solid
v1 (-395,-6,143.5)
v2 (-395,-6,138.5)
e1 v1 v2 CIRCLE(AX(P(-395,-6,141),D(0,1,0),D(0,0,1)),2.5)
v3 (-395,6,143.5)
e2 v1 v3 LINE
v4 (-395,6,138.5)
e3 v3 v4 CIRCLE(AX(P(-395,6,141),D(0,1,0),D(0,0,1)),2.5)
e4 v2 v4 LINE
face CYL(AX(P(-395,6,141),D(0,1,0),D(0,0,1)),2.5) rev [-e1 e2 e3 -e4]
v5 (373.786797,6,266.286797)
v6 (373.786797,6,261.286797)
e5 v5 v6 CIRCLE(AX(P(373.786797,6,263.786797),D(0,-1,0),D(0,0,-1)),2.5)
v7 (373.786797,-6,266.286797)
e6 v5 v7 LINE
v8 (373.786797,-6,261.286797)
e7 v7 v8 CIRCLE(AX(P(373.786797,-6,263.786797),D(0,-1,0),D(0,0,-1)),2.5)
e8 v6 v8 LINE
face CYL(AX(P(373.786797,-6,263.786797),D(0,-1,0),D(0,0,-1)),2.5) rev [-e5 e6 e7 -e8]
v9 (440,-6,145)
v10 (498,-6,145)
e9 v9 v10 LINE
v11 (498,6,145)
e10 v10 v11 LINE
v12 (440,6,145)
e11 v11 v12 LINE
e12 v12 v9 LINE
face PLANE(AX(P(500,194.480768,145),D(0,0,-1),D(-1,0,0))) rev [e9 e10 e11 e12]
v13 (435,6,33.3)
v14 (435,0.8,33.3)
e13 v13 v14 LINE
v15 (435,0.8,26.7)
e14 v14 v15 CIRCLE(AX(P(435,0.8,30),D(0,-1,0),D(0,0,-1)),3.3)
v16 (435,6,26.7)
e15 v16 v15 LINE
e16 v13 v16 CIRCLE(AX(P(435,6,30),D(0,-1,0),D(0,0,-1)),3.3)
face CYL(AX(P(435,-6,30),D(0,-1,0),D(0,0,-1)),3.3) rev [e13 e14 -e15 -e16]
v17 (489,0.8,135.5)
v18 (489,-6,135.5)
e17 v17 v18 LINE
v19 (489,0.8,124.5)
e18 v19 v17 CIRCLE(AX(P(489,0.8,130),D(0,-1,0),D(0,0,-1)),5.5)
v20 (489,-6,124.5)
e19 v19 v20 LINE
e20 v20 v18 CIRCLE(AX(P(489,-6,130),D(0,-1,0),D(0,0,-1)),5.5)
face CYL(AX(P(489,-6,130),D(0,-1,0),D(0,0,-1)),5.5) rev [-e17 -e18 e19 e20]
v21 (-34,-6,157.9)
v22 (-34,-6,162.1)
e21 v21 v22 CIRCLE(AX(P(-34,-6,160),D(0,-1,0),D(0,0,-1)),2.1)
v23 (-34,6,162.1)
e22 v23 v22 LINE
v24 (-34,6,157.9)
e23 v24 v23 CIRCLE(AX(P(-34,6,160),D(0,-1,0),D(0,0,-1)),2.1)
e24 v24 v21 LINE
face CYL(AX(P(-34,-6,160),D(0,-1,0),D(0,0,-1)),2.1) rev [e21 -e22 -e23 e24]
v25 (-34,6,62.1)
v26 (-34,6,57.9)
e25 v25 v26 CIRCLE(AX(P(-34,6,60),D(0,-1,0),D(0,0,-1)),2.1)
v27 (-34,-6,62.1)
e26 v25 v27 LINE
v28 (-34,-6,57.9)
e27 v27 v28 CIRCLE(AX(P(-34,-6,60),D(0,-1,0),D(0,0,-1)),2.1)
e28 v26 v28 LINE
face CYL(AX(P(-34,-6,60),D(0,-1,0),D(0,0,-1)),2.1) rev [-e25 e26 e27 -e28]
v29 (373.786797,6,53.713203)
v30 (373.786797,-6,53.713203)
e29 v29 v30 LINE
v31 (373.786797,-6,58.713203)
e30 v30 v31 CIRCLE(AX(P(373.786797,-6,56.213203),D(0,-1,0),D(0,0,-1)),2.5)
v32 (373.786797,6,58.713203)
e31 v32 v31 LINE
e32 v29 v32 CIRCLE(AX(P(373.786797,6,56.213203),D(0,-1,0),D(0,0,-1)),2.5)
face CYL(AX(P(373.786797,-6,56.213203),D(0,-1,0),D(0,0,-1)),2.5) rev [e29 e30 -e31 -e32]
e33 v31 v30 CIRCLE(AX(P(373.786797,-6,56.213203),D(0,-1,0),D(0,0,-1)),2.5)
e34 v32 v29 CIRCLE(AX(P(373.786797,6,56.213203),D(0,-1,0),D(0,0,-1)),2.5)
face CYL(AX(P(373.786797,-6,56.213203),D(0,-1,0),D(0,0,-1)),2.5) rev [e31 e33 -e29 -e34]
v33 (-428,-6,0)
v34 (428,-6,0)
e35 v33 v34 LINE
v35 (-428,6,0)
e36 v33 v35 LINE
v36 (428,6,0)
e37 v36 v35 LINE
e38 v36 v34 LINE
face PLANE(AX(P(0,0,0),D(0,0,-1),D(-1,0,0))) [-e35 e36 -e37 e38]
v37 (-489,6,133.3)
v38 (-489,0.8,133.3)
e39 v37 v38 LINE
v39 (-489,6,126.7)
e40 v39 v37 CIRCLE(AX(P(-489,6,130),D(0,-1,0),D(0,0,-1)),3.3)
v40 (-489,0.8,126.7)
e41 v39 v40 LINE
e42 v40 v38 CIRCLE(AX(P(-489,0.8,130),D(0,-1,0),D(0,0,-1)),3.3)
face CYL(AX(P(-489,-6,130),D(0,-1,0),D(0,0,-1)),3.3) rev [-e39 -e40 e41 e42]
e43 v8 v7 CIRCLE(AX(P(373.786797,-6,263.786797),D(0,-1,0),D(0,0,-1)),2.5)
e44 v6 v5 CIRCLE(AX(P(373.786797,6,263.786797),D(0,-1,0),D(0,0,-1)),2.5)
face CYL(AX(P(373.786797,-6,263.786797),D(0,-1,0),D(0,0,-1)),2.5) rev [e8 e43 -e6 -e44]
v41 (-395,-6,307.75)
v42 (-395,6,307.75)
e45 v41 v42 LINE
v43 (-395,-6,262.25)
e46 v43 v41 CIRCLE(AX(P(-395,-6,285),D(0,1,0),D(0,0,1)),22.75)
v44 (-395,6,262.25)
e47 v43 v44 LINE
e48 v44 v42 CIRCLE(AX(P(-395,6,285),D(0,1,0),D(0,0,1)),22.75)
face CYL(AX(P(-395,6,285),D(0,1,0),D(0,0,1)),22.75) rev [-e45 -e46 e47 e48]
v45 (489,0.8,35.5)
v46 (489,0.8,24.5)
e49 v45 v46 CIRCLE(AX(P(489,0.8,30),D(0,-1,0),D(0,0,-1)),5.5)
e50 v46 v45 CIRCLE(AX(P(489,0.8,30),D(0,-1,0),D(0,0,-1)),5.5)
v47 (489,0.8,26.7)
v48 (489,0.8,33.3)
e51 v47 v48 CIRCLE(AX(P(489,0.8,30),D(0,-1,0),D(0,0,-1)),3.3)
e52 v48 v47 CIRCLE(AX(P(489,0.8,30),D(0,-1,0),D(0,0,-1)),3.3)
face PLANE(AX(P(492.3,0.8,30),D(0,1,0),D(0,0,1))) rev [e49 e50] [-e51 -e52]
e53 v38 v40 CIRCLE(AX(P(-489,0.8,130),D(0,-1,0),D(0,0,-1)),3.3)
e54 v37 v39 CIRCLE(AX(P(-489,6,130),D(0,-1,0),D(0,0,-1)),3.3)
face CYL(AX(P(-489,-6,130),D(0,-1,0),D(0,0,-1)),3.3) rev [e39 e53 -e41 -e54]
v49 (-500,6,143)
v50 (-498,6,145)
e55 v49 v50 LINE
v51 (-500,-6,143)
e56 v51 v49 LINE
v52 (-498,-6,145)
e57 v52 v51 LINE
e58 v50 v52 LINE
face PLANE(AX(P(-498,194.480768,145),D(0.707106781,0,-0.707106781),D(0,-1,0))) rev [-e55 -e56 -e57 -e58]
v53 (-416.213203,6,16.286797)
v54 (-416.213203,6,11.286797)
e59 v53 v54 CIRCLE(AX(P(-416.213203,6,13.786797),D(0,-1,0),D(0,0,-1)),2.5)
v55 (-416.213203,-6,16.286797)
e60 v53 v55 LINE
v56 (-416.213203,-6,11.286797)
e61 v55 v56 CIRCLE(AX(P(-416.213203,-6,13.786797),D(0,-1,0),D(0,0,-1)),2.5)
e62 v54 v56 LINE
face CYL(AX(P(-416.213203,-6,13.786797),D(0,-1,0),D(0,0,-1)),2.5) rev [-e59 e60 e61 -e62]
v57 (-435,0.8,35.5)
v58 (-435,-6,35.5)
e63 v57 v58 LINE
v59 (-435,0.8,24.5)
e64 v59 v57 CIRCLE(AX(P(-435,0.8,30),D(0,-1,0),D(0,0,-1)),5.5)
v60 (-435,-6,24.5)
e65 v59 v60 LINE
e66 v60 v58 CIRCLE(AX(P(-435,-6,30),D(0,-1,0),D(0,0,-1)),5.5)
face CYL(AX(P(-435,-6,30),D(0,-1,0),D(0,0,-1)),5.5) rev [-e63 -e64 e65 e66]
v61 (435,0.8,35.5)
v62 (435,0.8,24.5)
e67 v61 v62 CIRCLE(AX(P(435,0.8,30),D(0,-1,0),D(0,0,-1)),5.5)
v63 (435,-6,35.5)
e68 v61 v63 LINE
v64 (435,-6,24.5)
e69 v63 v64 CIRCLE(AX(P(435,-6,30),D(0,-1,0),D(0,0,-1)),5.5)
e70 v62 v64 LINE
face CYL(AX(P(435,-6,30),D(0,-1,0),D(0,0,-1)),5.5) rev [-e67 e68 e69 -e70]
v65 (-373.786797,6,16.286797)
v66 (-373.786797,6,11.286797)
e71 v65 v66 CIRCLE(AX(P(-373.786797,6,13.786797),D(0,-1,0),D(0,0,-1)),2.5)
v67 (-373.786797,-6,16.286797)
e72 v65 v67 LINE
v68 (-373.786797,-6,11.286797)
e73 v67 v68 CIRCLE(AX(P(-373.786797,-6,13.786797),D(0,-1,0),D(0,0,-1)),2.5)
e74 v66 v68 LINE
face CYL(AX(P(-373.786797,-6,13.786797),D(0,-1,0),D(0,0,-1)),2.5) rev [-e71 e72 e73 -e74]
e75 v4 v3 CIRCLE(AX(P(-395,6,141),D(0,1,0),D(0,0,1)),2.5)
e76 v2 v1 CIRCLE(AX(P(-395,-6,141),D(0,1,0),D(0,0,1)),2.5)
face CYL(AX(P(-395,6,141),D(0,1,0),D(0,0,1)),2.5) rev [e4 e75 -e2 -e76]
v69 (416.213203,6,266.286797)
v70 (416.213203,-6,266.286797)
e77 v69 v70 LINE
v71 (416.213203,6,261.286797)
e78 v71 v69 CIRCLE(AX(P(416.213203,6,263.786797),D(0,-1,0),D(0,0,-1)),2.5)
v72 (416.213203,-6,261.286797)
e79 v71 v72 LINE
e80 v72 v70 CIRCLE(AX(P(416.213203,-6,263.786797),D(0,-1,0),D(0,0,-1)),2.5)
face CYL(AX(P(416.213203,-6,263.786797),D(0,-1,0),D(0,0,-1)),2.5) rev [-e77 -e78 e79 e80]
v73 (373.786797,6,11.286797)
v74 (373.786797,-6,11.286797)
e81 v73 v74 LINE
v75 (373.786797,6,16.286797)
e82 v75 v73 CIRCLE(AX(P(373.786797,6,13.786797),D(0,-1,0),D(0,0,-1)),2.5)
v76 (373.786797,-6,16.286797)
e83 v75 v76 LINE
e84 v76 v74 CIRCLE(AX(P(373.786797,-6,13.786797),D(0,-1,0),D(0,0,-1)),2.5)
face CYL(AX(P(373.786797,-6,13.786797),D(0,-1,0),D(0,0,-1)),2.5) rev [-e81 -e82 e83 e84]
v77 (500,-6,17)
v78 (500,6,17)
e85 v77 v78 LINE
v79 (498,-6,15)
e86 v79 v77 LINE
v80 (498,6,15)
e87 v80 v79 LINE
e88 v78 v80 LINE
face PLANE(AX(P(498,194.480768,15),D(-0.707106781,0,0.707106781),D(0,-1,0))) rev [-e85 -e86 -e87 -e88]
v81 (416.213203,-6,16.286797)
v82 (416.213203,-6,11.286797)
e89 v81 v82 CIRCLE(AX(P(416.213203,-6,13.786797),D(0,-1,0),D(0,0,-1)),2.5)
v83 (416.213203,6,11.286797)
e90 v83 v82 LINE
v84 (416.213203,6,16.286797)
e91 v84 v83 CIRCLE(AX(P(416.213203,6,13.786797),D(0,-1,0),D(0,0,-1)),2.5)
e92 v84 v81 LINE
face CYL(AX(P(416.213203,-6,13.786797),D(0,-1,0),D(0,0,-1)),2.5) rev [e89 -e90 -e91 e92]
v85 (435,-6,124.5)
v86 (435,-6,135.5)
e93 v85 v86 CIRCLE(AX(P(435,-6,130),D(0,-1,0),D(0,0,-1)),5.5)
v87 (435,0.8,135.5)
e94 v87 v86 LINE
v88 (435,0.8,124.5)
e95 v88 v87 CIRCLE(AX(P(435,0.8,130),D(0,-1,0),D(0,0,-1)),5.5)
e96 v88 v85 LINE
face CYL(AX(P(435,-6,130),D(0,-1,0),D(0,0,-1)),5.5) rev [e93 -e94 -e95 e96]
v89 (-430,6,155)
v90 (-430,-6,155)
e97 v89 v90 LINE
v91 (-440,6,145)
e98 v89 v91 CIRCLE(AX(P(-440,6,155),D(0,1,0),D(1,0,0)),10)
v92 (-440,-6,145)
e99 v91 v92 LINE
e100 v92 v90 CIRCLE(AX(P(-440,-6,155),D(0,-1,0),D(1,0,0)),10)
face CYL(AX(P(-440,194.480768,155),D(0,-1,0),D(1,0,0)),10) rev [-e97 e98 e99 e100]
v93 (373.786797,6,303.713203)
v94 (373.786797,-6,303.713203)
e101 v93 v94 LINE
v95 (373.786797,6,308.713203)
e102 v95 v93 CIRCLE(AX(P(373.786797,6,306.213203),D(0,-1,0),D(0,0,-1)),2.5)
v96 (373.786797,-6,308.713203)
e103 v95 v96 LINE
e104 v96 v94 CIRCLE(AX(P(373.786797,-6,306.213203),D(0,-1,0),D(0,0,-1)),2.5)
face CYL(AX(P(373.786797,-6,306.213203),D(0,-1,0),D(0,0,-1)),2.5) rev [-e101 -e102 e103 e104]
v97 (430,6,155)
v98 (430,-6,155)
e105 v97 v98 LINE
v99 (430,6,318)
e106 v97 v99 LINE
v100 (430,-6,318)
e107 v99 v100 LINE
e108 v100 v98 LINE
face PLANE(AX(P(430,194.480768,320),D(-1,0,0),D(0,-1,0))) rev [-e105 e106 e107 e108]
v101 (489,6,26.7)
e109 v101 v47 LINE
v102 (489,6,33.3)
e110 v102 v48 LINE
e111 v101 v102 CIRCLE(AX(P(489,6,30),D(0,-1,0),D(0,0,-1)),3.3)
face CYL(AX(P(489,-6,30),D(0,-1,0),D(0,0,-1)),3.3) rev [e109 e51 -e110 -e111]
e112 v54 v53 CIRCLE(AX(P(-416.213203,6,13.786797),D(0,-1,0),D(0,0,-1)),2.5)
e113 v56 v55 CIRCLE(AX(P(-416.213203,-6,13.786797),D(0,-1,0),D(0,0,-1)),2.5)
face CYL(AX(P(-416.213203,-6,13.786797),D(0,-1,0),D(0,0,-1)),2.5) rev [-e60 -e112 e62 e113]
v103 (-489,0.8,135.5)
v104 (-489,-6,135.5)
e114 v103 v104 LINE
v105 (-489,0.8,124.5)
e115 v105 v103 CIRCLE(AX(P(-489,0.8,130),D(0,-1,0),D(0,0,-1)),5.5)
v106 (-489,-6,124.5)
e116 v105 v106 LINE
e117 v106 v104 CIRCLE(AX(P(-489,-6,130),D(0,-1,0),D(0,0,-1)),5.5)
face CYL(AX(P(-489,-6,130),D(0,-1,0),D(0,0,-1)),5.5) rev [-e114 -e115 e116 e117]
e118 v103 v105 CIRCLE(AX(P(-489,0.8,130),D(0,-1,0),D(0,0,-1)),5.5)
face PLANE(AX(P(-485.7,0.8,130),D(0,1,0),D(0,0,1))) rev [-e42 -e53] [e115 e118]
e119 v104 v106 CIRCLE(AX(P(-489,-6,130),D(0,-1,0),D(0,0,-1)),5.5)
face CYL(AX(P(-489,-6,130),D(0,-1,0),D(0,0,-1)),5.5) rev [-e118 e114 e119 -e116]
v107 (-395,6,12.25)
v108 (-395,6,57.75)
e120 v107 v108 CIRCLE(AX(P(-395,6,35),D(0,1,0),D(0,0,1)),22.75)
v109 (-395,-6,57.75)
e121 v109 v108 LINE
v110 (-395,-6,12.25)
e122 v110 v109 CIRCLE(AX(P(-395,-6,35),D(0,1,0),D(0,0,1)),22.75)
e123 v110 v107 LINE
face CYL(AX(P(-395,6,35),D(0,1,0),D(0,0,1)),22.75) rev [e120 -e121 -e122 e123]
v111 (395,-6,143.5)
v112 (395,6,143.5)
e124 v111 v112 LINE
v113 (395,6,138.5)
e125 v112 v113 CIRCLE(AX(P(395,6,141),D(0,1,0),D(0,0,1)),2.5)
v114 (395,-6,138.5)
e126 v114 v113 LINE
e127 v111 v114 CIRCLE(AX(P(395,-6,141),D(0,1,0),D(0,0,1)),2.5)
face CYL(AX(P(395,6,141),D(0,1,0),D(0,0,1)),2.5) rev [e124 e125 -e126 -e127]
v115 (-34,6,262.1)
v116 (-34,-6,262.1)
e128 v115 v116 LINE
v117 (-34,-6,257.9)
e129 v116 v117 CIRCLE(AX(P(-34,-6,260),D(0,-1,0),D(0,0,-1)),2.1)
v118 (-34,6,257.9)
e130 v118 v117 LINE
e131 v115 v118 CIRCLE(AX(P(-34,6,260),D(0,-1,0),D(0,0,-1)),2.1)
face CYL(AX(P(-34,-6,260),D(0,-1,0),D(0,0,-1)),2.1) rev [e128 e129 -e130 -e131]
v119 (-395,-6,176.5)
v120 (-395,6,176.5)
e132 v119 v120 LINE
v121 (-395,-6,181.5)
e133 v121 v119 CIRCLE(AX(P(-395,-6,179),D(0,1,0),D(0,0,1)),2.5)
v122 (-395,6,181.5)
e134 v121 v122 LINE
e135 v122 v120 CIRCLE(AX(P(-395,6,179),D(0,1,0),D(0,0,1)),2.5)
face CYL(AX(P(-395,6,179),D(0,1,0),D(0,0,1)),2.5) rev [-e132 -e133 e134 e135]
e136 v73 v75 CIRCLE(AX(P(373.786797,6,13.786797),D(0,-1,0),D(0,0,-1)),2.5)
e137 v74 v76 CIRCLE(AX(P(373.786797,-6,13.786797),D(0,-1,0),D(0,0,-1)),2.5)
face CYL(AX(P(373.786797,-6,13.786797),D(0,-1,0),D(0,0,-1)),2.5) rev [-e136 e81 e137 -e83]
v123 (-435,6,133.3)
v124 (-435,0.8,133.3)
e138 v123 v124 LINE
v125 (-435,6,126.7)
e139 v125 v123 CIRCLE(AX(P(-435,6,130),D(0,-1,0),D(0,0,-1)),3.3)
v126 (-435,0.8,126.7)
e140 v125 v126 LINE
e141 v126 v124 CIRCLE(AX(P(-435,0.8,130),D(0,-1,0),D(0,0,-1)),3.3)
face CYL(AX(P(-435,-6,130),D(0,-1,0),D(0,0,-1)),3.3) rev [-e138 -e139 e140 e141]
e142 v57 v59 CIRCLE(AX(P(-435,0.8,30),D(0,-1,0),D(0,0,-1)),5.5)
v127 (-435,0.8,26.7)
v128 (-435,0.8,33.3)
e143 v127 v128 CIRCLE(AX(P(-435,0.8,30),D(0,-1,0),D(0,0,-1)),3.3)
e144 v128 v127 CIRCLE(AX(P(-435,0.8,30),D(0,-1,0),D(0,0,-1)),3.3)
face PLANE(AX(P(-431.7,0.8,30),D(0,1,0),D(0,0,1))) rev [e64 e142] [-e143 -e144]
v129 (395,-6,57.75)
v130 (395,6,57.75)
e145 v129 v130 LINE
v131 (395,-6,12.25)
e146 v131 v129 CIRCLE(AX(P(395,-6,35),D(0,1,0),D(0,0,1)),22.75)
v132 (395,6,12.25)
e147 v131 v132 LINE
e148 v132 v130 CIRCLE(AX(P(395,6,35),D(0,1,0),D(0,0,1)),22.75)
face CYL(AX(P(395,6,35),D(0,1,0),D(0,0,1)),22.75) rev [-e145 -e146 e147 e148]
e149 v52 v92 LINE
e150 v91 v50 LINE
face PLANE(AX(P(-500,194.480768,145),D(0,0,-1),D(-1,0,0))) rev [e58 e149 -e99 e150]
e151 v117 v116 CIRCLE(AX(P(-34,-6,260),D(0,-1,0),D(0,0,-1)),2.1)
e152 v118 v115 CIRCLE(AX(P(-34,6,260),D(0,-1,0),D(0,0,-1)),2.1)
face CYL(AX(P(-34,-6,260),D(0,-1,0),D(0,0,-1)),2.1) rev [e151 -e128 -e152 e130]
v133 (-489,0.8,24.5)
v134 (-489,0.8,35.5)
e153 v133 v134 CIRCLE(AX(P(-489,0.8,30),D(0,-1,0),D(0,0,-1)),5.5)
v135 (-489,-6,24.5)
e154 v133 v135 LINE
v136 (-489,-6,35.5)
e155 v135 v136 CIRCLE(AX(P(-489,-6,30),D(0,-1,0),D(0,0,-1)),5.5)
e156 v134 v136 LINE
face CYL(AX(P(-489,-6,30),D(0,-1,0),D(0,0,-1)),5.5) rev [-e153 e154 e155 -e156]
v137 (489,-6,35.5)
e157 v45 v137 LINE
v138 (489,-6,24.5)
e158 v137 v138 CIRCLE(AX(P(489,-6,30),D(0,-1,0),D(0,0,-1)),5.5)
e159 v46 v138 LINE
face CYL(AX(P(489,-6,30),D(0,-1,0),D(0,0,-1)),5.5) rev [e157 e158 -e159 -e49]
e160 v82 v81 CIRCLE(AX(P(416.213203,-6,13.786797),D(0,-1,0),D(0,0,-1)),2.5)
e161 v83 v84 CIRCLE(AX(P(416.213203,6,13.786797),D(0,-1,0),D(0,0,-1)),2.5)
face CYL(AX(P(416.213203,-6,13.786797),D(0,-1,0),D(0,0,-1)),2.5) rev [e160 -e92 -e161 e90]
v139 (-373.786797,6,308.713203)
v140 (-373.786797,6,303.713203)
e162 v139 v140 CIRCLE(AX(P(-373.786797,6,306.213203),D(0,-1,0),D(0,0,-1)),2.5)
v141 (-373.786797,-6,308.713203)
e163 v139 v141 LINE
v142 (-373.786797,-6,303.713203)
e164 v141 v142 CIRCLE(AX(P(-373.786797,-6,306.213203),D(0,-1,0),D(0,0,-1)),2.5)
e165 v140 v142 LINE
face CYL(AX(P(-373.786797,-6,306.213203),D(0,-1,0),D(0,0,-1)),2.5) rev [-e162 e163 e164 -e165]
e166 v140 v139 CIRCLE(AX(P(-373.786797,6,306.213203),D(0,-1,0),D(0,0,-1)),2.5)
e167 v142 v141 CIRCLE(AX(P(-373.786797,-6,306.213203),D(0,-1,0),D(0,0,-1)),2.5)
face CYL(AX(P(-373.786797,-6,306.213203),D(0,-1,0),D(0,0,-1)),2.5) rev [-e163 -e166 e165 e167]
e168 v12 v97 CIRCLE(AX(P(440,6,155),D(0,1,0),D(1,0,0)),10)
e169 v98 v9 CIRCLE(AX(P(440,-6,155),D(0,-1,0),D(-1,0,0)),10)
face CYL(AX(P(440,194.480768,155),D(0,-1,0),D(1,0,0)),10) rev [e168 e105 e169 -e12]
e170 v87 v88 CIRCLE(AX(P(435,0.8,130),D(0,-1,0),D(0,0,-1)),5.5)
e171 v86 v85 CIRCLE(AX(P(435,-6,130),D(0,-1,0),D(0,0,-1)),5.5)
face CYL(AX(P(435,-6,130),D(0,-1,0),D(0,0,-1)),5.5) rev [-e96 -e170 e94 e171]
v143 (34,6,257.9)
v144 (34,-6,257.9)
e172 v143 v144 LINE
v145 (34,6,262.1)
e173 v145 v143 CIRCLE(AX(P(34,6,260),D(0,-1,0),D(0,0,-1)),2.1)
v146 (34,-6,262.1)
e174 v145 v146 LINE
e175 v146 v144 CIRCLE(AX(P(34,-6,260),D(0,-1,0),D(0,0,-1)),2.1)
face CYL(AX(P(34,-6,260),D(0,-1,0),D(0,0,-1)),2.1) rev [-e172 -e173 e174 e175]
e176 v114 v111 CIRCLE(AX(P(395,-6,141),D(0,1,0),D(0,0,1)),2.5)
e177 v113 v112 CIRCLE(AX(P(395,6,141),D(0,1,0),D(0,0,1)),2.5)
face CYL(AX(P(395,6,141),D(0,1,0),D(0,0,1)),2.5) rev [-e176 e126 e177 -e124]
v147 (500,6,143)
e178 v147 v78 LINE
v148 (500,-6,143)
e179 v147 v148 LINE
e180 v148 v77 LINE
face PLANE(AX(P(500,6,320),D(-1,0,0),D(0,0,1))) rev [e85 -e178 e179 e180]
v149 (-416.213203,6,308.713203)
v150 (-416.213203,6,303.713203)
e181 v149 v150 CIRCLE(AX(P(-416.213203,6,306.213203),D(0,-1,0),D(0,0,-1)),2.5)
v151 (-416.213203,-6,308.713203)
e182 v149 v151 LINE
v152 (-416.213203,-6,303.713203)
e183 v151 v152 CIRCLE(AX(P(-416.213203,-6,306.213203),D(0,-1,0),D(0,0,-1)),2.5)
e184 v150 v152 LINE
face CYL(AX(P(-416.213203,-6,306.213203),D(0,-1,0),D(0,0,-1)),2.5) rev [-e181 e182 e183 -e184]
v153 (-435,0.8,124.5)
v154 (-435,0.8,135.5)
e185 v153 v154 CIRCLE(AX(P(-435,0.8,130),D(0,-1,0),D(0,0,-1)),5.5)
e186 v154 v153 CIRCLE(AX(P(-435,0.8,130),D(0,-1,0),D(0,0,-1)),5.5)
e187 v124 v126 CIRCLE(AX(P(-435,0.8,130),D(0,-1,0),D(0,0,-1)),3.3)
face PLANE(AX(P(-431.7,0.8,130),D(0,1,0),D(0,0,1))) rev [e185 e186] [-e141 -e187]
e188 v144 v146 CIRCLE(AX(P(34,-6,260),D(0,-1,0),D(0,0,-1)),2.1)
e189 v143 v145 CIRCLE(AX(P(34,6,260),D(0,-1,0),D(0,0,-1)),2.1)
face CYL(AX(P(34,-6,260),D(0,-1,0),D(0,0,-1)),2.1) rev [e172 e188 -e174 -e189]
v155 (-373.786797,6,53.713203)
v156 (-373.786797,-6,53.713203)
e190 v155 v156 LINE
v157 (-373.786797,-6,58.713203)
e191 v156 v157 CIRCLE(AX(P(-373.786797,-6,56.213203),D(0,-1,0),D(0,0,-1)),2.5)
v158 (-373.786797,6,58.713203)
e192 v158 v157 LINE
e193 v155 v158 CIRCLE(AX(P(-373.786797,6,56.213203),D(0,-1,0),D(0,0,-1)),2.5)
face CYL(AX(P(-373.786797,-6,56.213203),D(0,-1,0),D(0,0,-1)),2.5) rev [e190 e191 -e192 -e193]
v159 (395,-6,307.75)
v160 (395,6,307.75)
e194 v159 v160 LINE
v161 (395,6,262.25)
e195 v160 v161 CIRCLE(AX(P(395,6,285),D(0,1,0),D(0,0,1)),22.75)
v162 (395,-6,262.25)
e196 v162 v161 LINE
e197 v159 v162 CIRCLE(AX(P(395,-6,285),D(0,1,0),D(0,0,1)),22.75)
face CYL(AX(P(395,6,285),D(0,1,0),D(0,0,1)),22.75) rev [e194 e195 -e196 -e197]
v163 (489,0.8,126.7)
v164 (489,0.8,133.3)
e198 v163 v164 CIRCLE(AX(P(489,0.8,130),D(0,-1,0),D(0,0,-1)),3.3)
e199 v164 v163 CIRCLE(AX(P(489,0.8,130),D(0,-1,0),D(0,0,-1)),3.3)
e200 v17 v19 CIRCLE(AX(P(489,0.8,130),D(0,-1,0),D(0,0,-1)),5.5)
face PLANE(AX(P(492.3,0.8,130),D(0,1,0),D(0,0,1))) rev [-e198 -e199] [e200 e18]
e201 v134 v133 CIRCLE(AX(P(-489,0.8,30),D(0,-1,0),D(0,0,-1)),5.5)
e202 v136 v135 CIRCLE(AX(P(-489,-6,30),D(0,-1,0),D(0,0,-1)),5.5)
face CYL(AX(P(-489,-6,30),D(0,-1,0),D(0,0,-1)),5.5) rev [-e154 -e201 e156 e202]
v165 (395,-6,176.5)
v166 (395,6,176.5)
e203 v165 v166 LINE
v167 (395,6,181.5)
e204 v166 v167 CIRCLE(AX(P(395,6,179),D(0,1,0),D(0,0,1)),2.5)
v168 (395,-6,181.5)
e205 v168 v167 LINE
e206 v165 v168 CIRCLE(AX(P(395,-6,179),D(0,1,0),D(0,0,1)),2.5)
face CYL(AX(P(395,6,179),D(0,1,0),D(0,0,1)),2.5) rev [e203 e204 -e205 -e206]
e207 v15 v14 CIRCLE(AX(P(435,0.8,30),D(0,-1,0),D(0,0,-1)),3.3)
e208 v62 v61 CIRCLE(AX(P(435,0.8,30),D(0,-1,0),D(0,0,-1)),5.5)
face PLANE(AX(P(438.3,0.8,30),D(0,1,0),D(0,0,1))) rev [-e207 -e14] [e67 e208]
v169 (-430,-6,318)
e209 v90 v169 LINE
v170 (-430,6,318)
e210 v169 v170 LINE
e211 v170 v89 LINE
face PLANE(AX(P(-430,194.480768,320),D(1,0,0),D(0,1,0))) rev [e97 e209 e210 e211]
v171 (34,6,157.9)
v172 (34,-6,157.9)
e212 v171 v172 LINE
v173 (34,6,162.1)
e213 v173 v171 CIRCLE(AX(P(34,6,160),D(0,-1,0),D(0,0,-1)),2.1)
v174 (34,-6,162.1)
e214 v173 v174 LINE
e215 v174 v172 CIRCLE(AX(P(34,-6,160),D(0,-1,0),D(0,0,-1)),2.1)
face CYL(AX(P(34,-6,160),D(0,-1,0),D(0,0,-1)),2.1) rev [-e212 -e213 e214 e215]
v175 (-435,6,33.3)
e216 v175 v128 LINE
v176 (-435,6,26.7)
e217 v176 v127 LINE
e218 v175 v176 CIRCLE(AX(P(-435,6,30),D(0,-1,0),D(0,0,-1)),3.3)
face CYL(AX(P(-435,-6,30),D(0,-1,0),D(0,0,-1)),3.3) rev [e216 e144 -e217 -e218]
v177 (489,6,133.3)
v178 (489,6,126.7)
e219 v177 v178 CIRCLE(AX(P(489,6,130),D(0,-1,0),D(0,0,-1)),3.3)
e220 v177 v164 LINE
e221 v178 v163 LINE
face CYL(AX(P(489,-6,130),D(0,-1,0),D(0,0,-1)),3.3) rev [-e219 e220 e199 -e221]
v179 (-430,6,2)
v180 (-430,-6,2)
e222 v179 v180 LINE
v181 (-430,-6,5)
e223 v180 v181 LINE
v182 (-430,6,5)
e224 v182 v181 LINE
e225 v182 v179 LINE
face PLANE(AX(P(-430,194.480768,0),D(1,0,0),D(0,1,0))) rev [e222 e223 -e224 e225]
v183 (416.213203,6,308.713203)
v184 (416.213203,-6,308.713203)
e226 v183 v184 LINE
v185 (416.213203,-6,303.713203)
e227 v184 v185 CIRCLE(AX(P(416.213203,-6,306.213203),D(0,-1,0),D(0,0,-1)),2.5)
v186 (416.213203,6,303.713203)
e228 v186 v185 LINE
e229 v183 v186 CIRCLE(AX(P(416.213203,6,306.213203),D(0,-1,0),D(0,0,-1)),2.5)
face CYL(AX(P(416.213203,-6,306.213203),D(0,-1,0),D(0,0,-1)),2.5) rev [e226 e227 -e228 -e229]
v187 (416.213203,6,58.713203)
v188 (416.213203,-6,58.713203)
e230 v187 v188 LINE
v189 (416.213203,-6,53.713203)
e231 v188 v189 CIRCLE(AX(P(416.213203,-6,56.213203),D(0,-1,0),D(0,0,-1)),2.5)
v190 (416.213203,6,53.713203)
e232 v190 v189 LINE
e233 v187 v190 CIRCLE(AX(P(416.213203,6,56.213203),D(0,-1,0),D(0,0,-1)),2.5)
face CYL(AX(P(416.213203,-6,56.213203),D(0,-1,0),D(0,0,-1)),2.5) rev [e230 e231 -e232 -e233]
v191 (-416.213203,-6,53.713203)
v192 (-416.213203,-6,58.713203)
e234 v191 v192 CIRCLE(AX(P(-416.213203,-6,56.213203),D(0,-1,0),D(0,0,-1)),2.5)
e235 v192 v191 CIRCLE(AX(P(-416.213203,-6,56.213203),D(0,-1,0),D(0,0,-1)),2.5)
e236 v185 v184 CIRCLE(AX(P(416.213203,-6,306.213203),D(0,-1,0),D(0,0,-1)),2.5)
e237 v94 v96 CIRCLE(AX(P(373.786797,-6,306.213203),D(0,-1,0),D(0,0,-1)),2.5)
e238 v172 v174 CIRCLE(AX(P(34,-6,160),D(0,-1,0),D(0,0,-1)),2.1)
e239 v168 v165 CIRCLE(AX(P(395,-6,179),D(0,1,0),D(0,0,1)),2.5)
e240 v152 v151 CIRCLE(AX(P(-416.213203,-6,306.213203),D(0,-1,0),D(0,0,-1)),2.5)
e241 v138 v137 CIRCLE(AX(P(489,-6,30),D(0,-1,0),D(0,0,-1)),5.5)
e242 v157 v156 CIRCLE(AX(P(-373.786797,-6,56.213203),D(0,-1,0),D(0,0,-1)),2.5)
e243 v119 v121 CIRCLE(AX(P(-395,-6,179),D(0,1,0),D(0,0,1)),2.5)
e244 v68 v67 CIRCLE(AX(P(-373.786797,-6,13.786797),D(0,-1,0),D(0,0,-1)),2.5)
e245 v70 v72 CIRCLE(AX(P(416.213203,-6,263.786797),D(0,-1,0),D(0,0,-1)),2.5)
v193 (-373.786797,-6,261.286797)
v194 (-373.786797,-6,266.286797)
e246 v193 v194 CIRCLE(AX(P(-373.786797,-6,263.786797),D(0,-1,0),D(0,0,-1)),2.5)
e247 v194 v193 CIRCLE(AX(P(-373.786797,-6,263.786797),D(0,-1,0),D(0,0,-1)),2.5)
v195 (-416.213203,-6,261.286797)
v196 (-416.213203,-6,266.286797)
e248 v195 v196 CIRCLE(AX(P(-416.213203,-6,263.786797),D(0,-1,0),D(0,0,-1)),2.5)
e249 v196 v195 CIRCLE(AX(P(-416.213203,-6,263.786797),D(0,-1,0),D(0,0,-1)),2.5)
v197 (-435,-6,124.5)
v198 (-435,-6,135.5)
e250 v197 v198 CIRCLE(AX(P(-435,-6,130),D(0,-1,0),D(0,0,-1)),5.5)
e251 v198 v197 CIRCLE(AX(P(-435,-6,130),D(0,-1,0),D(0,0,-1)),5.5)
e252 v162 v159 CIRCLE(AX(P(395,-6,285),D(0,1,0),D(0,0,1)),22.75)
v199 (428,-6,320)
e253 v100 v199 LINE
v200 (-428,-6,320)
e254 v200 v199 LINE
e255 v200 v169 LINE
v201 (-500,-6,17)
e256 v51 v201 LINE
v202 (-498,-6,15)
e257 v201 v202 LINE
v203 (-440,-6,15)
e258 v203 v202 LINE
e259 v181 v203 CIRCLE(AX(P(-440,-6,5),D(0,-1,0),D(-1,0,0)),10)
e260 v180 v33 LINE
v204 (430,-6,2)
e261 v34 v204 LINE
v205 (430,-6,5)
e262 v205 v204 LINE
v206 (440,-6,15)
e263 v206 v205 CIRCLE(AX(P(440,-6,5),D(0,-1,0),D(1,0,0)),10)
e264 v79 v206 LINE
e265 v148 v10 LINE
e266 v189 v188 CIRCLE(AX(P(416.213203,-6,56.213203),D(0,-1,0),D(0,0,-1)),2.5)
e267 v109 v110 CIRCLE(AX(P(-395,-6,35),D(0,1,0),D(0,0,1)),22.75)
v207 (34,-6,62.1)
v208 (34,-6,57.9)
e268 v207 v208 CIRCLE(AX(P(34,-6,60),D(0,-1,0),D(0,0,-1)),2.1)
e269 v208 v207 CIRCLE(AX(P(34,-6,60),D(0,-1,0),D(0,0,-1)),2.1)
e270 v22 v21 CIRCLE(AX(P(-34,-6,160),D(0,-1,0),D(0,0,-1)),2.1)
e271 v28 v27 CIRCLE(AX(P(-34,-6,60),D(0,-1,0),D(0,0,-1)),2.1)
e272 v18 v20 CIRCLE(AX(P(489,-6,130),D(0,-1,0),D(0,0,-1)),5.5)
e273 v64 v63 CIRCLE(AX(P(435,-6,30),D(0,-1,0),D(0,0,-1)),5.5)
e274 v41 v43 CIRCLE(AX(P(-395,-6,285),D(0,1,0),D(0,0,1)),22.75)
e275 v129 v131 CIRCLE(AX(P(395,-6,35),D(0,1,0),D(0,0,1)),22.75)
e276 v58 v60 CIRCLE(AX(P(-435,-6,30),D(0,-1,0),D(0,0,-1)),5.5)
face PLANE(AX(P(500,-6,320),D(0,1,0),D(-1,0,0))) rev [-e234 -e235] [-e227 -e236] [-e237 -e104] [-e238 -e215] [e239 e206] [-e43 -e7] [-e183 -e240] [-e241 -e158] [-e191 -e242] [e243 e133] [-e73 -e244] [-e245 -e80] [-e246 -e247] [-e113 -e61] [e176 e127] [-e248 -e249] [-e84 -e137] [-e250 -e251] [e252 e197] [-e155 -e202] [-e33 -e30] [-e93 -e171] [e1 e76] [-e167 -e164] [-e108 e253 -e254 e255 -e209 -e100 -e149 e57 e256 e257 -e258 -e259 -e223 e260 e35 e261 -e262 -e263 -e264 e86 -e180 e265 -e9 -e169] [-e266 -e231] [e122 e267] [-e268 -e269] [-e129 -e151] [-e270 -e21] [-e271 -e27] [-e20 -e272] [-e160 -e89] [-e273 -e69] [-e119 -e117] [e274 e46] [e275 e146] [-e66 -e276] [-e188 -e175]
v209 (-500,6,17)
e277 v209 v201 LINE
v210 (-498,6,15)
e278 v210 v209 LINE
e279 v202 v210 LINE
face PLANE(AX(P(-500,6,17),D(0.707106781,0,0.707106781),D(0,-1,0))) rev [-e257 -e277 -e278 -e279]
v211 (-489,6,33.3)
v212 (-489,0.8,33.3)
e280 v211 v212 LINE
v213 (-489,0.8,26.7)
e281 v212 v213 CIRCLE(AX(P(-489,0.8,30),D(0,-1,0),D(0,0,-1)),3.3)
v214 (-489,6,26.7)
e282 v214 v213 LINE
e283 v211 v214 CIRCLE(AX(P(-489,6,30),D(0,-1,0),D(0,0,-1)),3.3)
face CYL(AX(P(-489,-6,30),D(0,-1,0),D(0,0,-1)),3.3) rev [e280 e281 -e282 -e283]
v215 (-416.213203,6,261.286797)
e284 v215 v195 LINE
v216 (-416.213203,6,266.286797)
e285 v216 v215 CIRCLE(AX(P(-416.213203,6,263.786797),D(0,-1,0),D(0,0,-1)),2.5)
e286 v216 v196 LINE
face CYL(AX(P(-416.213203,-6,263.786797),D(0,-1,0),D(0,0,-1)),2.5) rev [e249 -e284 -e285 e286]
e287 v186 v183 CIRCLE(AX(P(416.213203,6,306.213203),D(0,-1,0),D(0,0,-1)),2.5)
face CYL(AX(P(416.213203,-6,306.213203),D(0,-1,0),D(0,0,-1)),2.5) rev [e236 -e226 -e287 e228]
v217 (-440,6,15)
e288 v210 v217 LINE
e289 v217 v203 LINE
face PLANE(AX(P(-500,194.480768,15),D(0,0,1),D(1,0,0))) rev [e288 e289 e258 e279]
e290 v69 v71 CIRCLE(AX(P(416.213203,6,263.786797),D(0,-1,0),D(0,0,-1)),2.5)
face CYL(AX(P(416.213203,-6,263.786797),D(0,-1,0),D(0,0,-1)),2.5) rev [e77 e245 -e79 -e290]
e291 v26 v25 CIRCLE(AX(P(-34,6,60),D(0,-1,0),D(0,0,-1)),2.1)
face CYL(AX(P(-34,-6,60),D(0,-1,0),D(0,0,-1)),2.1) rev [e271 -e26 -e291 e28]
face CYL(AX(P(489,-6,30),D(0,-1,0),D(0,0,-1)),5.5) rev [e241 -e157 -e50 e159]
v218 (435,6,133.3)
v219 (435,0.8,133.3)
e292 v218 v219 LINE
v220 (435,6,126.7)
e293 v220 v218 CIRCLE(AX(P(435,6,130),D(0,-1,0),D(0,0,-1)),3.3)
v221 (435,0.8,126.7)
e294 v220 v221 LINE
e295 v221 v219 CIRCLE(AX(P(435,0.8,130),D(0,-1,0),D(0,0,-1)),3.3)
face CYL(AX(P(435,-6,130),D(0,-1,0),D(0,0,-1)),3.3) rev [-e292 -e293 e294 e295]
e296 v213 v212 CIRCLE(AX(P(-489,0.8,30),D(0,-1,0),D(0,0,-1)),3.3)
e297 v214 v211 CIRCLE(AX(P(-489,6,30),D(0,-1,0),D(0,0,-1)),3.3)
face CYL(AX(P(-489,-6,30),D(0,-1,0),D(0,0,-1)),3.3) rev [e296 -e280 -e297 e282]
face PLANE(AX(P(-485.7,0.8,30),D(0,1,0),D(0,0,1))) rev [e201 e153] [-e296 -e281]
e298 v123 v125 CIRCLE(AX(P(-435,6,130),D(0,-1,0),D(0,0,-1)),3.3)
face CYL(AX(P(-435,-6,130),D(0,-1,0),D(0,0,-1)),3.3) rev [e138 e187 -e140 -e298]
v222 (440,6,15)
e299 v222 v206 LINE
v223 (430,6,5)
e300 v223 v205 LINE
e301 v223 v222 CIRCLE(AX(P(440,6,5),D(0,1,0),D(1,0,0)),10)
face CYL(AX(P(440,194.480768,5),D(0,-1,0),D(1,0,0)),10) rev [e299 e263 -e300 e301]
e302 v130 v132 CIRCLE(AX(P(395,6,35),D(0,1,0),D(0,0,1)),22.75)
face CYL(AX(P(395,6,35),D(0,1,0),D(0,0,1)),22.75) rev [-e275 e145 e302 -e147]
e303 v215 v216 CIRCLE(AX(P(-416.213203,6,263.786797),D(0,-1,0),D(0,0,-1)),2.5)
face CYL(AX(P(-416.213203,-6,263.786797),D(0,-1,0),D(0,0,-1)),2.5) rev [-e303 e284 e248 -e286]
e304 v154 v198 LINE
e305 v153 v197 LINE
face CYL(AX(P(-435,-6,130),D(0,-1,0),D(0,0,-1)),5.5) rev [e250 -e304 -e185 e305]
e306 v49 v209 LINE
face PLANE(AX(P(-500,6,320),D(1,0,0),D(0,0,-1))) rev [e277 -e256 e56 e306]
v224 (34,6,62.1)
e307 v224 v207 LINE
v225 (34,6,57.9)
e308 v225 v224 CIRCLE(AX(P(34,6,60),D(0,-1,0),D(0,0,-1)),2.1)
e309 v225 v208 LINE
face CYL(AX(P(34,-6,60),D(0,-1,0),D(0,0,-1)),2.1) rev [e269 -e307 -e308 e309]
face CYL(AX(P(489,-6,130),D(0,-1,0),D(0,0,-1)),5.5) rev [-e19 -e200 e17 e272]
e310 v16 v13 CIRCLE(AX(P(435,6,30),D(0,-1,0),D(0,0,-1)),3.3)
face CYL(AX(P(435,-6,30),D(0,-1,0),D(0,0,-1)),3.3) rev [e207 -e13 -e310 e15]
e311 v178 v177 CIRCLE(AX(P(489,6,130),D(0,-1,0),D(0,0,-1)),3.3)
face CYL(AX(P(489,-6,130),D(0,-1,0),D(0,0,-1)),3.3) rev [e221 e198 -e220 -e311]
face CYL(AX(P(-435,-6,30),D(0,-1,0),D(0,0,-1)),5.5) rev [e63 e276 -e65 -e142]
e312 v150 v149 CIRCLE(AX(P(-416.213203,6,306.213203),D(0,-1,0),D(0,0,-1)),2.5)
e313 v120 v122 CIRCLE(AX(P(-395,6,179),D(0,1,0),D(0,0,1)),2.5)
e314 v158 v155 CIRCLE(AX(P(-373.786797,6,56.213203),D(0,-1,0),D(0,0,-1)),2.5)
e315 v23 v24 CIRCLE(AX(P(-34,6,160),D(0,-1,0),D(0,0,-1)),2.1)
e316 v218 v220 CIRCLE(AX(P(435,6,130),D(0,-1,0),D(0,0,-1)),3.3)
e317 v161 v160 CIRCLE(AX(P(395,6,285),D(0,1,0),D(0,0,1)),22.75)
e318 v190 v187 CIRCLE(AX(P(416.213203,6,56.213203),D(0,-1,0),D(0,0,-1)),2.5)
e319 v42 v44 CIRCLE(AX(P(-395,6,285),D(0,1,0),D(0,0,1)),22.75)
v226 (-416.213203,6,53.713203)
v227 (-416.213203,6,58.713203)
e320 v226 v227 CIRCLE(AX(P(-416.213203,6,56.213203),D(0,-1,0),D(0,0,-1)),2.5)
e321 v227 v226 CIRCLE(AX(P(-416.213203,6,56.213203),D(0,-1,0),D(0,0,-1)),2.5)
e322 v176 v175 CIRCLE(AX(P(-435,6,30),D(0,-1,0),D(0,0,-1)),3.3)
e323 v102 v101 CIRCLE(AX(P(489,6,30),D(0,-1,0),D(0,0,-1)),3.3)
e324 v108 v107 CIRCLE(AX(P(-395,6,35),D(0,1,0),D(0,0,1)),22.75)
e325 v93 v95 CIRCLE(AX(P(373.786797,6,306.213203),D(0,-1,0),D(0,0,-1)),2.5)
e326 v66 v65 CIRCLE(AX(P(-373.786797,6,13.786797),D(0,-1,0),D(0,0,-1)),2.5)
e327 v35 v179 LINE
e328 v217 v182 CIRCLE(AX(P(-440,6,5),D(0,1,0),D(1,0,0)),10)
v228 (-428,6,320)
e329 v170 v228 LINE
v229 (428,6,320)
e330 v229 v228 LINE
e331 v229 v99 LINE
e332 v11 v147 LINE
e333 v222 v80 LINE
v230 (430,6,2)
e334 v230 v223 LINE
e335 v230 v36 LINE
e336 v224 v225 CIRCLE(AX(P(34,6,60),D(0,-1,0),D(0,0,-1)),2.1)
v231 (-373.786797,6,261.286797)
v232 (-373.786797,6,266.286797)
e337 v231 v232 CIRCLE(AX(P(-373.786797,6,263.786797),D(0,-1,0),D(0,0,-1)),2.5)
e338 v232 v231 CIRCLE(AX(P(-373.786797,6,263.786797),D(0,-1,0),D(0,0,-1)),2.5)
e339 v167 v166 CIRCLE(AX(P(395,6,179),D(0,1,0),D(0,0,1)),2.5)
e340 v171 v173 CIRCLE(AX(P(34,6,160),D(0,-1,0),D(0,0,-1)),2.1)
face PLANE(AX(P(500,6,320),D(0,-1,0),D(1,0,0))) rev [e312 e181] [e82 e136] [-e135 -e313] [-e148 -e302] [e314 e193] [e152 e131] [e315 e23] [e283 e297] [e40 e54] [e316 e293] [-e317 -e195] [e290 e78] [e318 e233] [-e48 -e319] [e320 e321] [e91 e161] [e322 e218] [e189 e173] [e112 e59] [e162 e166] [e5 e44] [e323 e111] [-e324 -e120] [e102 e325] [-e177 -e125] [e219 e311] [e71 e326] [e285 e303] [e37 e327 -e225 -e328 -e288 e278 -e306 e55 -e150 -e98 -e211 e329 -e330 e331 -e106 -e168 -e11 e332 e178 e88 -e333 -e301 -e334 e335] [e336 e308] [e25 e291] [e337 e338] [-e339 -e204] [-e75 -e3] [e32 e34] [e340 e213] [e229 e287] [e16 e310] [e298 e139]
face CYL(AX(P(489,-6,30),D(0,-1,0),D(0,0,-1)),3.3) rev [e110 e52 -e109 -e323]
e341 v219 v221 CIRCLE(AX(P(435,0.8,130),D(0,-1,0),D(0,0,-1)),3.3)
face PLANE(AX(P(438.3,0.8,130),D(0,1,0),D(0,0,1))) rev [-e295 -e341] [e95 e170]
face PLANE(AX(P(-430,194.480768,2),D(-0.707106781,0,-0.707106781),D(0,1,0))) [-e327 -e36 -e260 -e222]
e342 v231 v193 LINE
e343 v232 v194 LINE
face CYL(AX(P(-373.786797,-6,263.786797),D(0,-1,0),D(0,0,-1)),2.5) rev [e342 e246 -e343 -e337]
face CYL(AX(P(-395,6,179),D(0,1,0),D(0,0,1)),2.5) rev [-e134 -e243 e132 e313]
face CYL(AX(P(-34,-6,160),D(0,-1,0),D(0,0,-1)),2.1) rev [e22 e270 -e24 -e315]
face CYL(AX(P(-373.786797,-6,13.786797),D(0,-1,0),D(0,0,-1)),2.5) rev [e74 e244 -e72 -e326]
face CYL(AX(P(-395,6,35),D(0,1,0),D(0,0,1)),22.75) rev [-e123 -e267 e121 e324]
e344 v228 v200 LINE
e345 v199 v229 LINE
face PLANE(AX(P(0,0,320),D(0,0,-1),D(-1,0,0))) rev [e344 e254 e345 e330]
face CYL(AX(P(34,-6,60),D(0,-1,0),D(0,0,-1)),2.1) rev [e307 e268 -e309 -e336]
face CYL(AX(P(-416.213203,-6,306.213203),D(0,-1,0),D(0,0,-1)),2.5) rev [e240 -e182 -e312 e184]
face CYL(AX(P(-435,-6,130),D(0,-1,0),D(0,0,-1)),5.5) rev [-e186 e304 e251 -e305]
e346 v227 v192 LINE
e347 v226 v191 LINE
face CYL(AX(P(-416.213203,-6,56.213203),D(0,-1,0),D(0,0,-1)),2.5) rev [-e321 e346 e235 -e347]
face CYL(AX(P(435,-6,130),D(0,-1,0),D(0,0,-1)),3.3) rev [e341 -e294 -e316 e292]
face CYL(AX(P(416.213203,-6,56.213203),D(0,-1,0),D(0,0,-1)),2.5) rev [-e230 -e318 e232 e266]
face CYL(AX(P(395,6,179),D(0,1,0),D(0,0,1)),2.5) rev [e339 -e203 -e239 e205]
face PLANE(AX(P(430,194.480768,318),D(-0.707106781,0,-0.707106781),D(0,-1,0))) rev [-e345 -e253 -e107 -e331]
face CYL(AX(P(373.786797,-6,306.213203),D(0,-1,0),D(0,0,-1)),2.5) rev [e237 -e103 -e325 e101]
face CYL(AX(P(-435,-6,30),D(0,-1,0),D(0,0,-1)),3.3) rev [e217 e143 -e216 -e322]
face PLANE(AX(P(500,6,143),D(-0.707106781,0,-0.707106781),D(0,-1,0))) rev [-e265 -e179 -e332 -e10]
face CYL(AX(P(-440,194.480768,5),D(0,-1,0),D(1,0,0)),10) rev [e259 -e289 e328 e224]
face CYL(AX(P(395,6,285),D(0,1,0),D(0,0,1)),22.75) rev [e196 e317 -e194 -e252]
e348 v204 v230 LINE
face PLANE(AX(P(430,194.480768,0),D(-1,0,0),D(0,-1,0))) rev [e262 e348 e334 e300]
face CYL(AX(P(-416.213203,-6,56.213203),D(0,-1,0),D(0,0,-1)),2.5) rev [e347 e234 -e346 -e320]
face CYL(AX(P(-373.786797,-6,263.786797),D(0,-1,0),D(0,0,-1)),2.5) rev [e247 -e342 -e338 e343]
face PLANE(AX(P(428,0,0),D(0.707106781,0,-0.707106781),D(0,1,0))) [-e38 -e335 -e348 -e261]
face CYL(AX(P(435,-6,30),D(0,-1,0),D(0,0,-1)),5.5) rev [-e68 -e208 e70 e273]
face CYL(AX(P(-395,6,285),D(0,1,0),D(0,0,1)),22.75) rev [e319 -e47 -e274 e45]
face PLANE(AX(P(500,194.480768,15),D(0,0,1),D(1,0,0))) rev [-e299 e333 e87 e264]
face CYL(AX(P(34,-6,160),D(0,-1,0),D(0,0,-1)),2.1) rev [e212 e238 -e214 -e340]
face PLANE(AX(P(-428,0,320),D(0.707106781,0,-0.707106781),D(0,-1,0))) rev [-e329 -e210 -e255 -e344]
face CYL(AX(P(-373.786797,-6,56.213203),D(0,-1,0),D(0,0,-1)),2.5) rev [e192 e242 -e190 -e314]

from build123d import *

# Parameters (mm, degrees)
SKETCH_1_W                = 1000
SKETCH_1_H                = 12
EXTRUDE_1_DEPTH           = 320
HOLE_WIZARD_M5_1_D        = 4.2
HOLE_WIZARD_25_0_45_5_1_D = 45.5
CUT_EXTRUDE_2_DEPTH       = 12
HOLE_WIZARD_2_D           = 6.6
HOLE_WIZARD_2_CBORE_D     = 11
HOLE_WIZARD_2_CBORE_DEPTH = 6.8
CHAMFER_1_SIZE            = 2
HOLE_WIZARD_M6_1_D        = 5
HOLE_WIZARD_M6_2_D        = 5


with BuildPart() as part:
    # 草图1 → 凸台-拉伸1 (new body)
    with BuildSketch(Plane.XY):
        Rectangle(SKETCH_1_W, SKETCH_1_H)
    extrude(amount=EXTRUDE_1_DEPTH)

    # M5 螺纹孔1 (through all)
    with Locations(Plane(origin=(0, -6, 0), x_dir=(-1, 0, 0), z_dir=(0, -1, 0))):
        with Locations((34, -60), (34, -260), (-34, -260), (34, -160), (-34, -160), (-34, -60)):
            Hole(HOLE_WIZARD_M5_1_D / 2)

    # Ø25.0 (45.5) 直径孔1 (through all)
    with Locations(Plane(origin=(0, 6, 0), x_dir=(1, 0, 0), z_dir=(0, 1, 0))):
        with Locations((395, -285), (395, -35), (-395, -35), (-395, -285)):
            Hole(HOLE_WIZARD_25_0_45_5_1_D / 2)

    # 草图22 → 切除-拉伸2 (cut)
    with BuildSketch(Plane.XZ.offset(6)):
        with BuildLine():
            Line((500, 320), (430, 320))
            Line((430, 320), (430, 155))
            ThreePointArc((430, 155), (432.928932188, 147.928932188), (440, 145))
            Line((440, 145), (500, 145))
            Line((500, 145), (500, 320))
        make_face()
        with BuildLine():
            Line((-430, 320), (-430, 155))
            ThreePointArc((-430, 155), (-432.928932188, 147.928932188), (-440, 145))
            Line((-440, 145), (-500, 145))
            Line((-500, 145), (-500, 320))
            Line((-500, 320), (-430, 320))
        make_face()
        with BuildLine():
            Line((-430, 0), (-430, 5))
            ThreePointArc((-430, 5), (-432.928932188, 12.071067812), (-440, 15))
            Line((-440, 15), (-500, 15))
            Line((-500, 15), (-500, 0))
            Line((-500, 0), (-430, 0))
        make_face()
        with BuildLine():
            Line((500, 0), (430, 0))
            Line((430, 0), (430, 5))
            ThreePointArc((430, 5), (432.928932188, 12.071067812), (440, 15))
            Line((440, 15), (500, 15))
            Line((500, 15), (500, 0))
        make_face()
    extrude(amount=-CUT_EXTRUDE_2_DEPTH, mode=Mode.SUBTRACT)

    # 打孔尺寸(%根据)内六角圆柱头螺钉的类型2 (through all)
    with Locations(Plane.XZ.offset(6)):
        with Locations((489, 130), (489, 30), (435, 30), (435, 130), (-435, 130), (-435, 30), (-489, 30), (-489, 130)):
            CounterBoreHole(HOLE_WIZARD_2_D / 2, HOLE_WIZARD_2_CBORE_D / 2, HOLE_WIZARD_2_CBORE_DEPTH)

    # 倒角1
    chamfer_1_edges = [part.edges().sort_by_distance(p)[0] for p in [
        (-430, 0, 0),
        (-500, 0, 15),
        (500, 0, 145),
        (430, 0, 320),
        (-500, 0, 145),
        (-430, 0, 320),
        (500, 0, 15),
        (430, 0, 0),
    ]]
    chamfer(chamfer_1_edges, length=CHAMFER_1_SIZE)

    # M6 螺纹孔1 (through all)
    with Locations(Plane(origin=(0, 6, 0), x_dir=(1, 0, 0), z_dir=(0, 1, 0))):
        with Locations((-395, -141), (-395, -179), (395, -179), (395, -141)):
            Hole(HOLE_WIZARD_M6_1_D / 2)

    # M6 螺纹孔2 (through all)
    with Locations(Plane(origin=(0, -6, 0), x_dir=(-1, 0, 0), z_dir=(0, -1, 0))):
        with Locations((-416.213203436, -263.786796564), (-373.786796564, -263.786796564), (-373.786796564, -306.213203436), (-416.213203436, -306.213203436), (373.786796564, -263.786796564), (416.213203436, -263.786796564), (416.213203436, -306.213203436), (373.786796564, -306.213203436), (373.786796564, -13.786796564), (416.213203436, -13.786796564), (416.213203436, -56.213203436), (373.786796564, -56.213203436), (-416.213203436, -13.786796564), (-373.786796564, -13.786796564), (-373.786796564, -56.213203436), (-416.213203436, -56.213203436)):
            Hole(HOLE_WIZARD_M6_2_D / 2)


solid = part.part
